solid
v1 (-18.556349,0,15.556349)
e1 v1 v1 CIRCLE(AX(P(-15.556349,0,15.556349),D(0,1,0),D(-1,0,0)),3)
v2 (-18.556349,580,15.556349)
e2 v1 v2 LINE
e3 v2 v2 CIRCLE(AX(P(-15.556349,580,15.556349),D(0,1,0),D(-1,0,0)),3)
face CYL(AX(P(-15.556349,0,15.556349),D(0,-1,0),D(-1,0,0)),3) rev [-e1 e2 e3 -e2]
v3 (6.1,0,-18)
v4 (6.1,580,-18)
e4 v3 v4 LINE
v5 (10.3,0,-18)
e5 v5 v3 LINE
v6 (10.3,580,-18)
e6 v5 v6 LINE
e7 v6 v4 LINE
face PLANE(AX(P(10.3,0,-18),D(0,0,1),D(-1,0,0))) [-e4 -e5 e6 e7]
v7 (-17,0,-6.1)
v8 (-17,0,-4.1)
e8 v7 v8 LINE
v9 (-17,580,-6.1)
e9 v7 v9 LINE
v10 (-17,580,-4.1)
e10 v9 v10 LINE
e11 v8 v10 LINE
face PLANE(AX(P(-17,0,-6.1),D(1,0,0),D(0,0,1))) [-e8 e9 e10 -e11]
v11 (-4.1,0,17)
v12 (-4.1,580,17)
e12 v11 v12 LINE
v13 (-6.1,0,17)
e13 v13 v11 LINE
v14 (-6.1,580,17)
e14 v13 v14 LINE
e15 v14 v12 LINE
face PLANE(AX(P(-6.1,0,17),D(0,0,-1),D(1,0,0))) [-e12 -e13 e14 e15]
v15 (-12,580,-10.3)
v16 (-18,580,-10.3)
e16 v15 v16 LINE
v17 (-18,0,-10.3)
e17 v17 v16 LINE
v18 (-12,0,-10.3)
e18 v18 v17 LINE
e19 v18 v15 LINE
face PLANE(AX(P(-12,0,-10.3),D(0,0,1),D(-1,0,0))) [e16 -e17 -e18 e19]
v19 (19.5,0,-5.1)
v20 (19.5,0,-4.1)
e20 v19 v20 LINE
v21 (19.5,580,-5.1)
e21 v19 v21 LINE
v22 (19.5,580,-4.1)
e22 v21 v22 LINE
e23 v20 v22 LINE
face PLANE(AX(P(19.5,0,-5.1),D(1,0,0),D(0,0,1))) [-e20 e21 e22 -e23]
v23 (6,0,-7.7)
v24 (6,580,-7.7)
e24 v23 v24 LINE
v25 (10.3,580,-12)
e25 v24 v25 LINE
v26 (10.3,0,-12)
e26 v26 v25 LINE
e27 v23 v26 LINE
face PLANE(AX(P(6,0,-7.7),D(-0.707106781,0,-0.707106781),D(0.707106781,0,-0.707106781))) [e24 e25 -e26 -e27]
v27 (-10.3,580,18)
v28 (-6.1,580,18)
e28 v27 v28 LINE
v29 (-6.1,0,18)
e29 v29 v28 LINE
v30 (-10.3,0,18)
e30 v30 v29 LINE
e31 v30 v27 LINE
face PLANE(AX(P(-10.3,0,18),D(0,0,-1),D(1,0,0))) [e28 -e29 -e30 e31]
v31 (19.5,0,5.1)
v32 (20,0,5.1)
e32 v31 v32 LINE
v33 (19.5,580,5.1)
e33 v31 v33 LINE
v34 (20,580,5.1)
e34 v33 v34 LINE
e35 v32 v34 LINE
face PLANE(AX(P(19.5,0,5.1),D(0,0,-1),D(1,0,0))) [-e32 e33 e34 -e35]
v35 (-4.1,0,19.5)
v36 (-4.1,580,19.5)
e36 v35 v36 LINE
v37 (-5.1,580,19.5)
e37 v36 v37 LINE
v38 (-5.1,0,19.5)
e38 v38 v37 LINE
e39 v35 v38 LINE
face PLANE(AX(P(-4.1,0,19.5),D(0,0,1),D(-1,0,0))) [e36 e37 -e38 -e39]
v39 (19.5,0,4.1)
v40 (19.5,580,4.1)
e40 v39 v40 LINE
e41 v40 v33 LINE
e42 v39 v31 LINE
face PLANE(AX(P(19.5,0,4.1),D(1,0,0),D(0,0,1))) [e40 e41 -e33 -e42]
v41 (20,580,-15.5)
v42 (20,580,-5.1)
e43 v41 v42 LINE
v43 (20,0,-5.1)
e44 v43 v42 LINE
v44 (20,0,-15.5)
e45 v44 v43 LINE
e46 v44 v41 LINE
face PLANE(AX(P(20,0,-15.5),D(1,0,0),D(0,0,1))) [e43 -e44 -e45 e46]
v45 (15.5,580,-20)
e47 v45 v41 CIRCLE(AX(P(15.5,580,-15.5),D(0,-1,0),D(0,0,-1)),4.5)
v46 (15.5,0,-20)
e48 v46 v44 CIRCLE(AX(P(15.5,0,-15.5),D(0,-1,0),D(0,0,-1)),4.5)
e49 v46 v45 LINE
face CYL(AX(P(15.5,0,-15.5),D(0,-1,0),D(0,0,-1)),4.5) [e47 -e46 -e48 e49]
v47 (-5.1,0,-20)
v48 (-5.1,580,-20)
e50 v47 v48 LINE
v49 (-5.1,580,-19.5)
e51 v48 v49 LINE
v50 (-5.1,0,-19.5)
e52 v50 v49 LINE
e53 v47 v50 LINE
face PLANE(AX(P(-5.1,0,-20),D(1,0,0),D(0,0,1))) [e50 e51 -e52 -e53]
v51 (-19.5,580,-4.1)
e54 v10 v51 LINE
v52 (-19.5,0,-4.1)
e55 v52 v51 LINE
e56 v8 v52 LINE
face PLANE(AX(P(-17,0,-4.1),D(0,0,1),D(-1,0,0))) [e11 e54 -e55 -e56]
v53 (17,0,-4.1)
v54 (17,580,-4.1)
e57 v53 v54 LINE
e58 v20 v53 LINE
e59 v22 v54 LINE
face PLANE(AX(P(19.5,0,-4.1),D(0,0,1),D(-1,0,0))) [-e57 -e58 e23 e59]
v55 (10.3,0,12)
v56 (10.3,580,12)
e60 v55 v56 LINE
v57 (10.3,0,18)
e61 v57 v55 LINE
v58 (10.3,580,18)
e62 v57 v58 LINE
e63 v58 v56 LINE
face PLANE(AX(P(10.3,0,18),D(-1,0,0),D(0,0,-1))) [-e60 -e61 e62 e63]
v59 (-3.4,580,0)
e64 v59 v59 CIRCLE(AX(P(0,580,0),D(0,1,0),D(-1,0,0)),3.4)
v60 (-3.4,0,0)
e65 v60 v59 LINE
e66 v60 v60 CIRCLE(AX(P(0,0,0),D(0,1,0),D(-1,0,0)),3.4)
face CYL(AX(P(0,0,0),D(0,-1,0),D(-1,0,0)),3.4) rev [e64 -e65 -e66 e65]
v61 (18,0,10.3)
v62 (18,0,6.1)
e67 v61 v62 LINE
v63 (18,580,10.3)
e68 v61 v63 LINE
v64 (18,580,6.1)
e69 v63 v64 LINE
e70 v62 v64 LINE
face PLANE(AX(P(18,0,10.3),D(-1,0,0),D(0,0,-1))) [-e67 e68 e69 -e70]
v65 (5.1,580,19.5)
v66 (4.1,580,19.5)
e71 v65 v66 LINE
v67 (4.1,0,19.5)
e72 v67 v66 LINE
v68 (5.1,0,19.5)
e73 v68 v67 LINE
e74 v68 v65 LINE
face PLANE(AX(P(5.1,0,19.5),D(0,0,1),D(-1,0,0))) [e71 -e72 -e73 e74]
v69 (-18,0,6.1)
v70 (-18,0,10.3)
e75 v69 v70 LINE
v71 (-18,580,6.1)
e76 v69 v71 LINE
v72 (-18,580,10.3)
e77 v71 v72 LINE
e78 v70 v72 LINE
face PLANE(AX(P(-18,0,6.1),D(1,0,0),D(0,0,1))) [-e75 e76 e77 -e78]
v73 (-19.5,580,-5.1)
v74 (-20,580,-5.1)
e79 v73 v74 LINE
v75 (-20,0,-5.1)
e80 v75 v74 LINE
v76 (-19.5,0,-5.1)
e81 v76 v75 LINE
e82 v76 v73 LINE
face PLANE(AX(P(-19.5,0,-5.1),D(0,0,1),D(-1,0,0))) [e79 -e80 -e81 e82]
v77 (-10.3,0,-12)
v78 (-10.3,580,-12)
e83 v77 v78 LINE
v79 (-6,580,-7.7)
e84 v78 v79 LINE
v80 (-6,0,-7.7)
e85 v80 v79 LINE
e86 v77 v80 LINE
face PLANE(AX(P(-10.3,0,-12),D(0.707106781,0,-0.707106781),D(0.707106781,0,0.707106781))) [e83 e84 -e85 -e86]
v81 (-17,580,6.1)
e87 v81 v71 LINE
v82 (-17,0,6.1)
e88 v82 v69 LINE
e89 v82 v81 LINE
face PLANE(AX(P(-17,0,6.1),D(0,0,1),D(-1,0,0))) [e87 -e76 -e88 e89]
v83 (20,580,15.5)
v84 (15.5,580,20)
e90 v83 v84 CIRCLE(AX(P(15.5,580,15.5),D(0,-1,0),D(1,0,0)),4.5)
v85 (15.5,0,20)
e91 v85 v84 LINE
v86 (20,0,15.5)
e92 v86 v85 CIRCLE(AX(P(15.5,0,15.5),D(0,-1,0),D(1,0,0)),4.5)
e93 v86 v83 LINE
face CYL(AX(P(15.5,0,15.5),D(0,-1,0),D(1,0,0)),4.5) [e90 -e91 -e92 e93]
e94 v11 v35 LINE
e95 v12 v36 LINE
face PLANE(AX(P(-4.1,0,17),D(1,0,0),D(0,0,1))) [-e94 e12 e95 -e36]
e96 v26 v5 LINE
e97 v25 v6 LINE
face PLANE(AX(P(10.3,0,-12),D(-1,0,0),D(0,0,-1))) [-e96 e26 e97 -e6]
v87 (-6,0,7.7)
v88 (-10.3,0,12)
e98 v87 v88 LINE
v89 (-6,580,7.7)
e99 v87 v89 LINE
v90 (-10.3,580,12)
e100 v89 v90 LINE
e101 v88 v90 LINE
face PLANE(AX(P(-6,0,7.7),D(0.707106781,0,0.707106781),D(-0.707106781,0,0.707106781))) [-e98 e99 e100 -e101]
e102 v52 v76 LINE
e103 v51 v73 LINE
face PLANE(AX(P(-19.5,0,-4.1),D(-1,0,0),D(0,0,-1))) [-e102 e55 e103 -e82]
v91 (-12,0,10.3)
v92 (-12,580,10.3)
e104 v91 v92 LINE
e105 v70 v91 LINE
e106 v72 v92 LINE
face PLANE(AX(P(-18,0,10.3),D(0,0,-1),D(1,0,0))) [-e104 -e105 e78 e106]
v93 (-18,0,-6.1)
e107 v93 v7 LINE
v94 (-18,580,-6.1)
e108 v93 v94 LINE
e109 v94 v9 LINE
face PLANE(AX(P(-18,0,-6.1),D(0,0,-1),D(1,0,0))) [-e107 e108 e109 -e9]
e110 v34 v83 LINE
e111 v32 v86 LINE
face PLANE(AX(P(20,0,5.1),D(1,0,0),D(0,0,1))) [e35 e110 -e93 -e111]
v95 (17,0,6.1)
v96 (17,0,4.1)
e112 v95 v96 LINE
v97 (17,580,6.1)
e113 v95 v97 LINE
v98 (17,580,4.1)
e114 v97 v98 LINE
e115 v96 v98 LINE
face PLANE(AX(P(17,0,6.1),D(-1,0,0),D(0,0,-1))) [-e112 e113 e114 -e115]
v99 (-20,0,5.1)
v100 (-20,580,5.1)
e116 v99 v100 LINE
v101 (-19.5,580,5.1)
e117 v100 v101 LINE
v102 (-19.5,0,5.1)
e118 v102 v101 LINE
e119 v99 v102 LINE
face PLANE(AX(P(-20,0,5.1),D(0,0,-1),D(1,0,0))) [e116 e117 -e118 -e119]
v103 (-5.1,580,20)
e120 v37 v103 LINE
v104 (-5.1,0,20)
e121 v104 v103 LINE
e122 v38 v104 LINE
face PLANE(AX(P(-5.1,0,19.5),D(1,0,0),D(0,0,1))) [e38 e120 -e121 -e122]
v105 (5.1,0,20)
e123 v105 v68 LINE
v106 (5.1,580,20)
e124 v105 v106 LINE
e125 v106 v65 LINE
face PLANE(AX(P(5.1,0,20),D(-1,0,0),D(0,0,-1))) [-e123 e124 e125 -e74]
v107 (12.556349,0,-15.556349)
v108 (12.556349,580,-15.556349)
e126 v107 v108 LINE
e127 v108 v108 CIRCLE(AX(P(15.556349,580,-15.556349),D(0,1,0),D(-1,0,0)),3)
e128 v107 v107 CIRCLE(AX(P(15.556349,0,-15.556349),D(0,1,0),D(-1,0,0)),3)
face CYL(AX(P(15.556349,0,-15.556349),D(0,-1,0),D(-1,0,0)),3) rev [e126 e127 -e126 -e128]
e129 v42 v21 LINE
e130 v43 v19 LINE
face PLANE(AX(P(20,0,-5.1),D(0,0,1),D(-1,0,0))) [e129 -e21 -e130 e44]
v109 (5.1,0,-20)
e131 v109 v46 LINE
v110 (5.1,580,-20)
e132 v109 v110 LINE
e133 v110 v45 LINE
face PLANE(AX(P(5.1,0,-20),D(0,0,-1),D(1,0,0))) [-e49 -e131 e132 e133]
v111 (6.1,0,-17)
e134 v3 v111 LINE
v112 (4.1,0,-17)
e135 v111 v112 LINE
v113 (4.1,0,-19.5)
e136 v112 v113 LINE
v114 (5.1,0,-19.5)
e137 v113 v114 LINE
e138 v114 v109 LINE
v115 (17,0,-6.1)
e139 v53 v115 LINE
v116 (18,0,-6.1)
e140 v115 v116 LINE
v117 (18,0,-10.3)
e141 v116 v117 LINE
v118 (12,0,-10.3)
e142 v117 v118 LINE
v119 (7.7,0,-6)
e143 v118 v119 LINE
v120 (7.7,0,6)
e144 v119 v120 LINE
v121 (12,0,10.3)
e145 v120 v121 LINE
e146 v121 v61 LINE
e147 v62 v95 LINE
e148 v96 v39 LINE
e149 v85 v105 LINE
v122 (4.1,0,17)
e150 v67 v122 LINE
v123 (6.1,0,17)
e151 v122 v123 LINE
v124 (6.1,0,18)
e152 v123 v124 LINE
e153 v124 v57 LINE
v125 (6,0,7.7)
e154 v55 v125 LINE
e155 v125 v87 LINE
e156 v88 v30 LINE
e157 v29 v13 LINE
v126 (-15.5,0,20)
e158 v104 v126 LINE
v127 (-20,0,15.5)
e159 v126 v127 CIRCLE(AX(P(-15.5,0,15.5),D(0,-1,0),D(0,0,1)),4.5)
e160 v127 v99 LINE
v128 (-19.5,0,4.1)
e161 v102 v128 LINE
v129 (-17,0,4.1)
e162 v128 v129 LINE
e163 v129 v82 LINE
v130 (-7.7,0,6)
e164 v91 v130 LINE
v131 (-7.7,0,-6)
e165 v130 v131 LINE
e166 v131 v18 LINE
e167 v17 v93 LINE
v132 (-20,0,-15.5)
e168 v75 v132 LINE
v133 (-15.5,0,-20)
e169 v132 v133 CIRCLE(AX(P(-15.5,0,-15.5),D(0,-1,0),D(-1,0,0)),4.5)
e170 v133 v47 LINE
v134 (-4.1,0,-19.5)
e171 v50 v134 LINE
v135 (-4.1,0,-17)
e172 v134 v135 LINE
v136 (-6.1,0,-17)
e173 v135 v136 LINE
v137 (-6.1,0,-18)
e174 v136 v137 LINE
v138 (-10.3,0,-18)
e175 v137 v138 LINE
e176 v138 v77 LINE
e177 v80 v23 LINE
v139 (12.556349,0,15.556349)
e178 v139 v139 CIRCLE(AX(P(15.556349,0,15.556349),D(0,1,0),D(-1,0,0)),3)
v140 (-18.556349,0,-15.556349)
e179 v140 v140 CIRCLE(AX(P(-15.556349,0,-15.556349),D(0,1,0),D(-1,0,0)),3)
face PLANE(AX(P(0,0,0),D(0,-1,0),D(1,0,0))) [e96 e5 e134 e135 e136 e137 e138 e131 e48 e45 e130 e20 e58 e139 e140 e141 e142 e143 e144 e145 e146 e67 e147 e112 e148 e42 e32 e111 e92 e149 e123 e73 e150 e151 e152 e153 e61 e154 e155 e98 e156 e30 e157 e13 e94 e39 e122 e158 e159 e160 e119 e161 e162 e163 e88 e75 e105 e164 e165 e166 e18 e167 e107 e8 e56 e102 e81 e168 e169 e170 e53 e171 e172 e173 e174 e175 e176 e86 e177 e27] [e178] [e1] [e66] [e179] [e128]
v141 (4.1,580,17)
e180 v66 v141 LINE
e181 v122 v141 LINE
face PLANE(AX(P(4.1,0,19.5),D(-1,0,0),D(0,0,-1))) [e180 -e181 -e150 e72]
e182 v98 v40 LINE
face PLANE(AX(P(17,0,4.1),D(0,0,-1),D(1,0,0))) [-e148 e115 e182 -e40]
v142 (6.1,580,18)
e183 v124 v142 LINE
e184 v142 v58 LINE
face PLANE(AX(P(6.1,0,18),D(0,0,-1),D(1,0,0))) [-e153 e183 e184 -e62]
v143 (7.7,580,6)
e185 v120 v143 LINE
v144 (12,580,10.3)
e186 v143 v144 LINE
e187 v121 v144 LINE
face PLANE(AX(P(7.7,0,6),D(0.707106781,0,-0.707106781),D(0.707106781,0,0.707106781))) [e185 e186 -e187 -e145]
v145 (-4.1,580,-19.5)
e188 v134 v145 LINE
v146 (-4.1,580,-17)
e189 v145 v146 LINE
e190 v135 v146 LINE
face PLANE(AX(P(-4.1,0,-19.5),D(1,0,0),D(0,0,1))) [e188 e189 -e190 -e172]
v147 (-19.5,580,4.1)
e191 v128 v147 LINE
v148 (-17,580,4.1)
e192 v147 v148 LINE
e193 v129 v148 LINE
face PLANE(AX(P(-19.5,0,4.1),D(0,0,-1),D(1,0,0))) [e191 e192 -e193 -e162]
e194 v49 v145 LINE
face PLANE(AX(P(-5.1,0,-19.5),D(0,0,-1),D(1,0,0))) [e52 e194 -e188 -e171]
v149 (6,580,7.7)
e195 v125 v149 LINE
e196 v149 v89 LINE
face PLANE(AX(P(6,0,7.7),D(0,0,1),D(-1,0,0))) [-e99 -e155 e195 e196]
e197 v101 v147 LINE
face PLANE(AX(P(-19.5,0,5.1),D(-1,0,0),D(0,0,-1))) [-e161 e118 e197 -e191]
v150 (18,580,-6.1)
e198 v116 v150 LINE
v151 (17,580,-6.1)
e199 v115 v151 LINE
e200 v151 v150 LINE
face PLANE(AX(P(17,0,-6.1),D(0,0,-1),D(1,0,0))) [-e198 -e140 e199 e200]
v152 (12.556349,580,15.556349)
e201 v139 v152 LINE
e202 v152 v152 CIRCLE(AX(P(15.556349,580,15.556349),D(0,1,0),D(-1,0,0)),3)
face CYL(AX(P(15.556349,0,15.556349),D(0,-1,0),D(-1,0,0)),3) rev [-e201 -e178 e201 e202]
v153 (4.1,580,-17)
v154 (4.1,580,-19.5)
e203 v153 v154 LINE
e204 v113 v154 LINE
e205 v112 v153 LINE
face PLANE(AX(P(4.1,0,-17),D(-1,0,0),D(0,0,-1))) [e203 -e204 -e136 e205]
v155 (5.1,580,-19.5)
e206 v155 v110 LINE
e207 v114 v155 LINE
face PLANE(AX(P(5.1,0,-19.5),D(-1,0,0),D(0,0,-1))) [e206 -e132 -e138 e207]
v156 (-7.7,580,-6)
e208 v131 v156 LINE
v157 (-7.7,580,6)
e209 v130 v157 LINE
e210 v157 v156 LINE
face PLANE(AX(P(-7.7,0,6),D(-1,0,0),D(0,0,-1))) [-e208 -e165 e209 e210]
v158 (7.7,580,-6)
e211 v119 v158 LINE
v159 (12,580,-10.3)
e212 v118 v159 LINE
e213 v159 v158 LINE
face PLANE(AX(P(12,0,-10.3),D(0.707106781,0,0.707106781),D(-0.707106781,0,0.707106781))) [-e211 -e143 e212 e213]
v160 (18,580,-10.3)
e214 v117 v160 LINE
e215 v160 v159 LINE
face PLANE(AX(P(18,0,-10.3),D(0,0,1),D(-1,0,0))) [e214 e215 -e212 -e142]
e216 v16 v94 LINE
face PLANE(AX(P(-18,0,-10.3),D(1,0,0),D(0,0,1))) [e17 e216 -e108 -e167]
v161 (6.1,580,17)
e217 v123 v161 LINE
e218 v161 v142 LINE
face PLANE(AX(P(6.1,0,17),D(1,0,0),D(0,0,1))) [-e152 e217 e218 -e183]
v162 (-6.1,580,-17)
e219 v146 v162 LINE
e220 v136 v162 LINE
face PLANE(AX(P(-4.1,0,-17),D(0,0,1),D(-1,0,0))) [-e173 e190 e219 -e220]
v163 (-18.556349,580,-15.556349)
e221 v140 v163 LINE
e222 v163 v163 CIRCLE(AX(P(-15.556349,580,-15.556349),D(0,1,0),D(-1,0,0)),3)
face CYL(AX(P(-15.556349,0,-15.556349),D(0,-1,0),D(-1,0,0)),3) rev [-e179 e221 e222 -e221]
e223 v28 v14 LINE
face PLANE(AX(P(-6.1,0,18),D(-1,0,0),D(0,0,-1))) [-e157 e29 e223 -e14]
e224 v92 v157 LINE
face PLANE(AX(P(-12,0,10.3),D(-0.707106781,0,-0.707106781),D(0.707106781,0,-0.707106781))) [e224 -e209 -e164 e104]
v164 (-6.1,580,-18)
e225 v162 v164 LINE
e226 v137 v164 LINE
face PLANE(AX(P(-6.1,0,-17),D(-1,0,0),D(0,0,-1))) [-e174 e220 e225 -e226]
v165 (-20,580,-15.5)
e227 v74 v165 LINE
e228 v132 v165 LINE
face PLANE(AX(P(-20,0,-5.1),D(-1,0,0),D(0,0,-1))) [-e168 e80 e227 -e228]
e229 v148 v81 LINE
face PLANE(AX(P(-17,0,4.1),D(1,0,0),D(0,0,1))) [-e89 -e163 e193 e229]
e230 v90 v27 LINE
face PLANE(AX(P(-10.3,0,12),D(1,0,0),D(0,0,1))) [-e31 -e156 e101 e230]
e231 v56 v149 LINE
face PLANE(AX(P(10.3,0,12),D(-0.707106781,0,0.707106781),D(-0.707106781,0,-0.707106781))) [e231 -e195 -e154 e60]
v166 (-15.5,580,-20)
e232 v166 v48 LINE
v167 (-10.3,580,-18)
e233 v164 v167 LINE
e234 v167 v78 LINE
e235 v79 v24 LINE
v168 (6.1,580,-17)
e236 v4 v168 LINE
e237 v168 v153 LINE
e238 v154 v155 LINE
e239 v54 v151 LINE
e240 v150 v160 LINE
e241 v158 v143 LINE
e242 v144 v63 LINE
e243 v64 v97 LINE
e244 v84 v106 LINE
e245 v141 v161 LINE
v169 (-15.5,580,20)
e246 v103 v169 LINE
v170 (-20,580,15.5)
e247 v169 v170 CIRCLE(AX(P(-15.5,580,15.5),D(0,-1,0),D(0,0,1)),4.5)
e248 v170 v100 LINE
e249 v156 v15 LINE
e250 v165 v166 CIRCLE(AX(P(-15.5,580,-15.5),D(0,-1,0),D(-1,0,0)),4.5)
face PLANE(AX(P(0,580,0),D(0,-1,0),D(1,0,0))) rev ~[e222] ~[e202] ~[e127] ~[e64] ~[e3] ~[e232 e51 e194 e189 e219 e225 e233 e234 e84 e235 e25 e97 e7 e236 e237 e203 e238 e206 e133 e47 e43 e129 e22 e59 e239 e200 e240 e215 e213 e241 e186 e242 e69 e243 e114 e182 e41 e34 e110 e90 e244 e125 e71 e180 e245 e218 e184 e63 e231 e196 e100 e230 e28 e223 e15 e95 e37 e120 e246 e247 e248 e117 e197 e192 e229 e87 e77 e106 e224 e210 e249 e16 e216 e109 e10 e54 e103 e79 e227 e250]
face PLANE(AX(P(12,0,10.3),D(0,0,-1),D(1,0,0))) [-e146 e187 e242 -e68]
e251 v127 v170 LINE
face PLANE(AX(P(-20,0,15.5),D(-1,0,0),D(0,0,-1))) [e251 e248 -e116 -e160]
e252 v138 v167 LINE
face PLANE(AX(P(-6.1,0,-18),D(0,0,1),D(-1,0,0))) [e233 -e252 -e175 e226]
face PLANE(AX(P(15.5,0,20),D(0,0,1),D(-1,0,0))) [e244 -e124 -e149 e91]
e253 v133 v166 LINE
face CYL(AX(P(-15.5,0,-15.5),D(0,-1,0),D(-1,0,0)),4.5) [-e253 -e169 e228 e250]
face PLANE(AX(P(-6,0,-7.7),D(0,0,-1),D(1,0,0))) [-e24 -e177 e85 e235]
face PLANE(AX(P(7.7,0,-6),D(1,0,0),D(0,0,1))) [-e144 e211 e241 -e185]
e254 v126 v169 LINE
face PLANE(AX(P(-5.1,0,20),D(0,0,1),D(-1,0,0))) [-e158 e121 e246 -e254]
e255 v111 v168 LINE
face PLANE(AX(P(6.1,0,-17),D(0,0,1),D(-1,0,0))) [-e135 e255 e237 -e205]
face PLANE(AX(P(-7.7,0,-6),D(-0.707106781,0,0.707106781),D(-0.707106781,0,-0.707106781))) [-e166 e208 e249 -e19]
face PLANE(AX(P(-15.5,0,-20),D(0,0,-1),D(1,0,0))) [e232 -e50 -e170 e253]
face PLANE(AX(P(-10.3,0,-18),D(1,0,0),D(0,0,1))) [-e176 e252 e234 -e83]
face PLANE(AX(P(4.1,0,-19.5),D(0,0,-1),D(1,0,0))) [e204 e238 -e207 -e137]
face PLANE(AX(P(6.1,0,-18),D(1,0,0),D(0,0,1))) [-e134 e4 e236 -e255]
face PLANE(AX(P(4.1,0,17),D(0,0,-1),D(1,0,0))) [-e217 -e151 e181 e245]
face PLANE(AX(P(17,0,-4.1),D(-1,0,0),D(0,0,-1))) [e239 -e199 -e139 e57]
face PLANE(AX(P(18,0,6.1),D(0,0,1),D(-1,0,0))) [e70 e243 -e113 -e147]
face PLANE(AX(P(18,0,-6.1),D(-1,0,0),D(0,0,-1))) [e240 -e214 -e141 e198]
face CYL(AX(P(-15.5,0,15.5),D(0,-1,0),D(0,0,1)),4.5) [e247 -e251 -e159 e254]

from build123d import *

# Parameters (mm, degrees)
SKETCH16_R     = 3.4
SKETCH16_R_2   = 3
MEMBER_1_DEPTH = 580


with BuildPart() as part:
    # Sketch16 → Member 1 (new body)
    with BuildSketch(Plane(origin=(0, 0, 0), x_dir=(-1, 0, 0), z_dir=(0, 1, 0))):
        with BuildLine():
            Line((-5.1, 20), (-5.1, 19.5))
            Line((-5.1, 19.5), (-4.1, 19.5))
            Line((-4.1, 19.5), (-4.1, 17))
            Line((-4.1, 17), (-6.1, 17))
            Line((-6.1, 17), (-6.1, 18))
            Line((-6.1, 18), (-10.3, 18))
            Line((-10.3, 18), (-10.3, 12))
            Line((-10.3, 12), (-6, 7.7))
            Line((-6, 7.7), (6, 7.7))
            Line((6, 7.7), (10.3, 12))
            Line((10.3, 12), (10.3, 18))
            Line((10.3, 18), (6.1, 18))
            Line((6.1, 18), (6.1, 17))
            Line((6.1, 17), (4.1, 17))
            Line((4.1, 17), (4.1, 19.5))
            Line((4.1, 19.5), (5.1, 19.5))
            Line((5.1, 19.5), (5.1, 20))
            Line((5.1, 20), (15.5, 20))
            ThreePointArc((15.5, 20), (18.681980515, 18.681980515), (20, 15.5))
            Line((20, 15.5), (20, 5.1))
            Line((20, 5.1), (19.5, 5.1))
            Line((19.5, 5.1), (19.5, 4.1))
            Line((19.5, 4.1), (17, 4.1))
            Line((17, 4.1), (17, 6.1))
            Line((17, 6.1), (18, 6.1))
            Line((18, 6.1), (18, 10.3))
            Line((18, 10.3), (12, 10.3))
            Line((12, 10.3), (7.7, 6))
            Line((7.7, 6), (7.7, -6))
            Line((7.7, -6), (12, -10.3))
            Line((12, -10.3), (18, -10.3))
            Line((18, -10.3), (18, -6.1))
            Line((18, -6.1), (17, -6.1))
            Line((17, -6.1), (17, -4.1))
            Line((17, -4.1), (19.5, -4.1))
            Line((19.5, -4.1), (19.5, -5.1))
            Line((19.5, -5.1), (20, -5.1))
            Line((20, -5.1), (20, -15.5))
            ThreePointArc((20, -15.5), (18.681980515, -18.681980515), (15.5, -20))
            Line((15.5, -20), (5.1, -20))
            Line((5.1, -20), (5.1, -19.5))
            Line((5.1, -19.5), (4.1, -19.5))
            Line((4.1, -19.5), (4.1, -17))
            Line((4.1, -17), (6.1, -17))
            Line((6.1, -17), (6.1, -18))
            Line((6.1, -18), (10.3, -18))
            Line((10.3, -18), (10.3, -12))
            Line((10.3, -12), (6, -7.7))
            Line((6, -7.7), (-6, -7.7))
            Line((-6, -7.7), (-10.3, -12))
            Line((-10.3, -12), (-10.3, -18))
            Line((-10.3, -18), (-6.1, -18))
            Line((-6.1, -18), (-6.1, -17))
            Line((-6.1, -17), (-4.1, -17))
            Line((-4.1, -17), (-4.1, -19.5))
            Line((-4.1, -19.5), (-5.1, -19.5))
            Line((-5.1, -19.5), (-5.1, -20))
            Line((-5.1, -20), (-15.5, -20))
            ThreePointArc((-15.5, -20), (-18.681980515, -18.681980515), (-20, -15.5))
            Line((-20, -15.5), (-20, -5.1))
            Line((-20, -5.1), (-19.5, -5.1))
            Line((-19.5, -5.1), (-19.5, -4.1))
            Line((-19.5, -4.1), (-17, -4.1))
            Line((-17, -4.1), (-17, -6.1))
            Line((-17, -6.1), (-18, -6.1))
            Line((-18, -6.1), (-18, -10.3))
            Line((-18, -10.3), (-12, -10.3))
            Line((-12, -10.3), (-7.7, -6))
            Line((-7.7, -6), (-7.7, 6))
            Line((-7.7, 6), (-12, 10.3))
            Line((-12, 10.3), (-18, 10.3))
            Line((-18, 10.3), (-18, 6.1))
            Line((-18, 6.1), (-17, 6.1))
            Line((-17, 6.1), (-17, 4.1))
            Line((-17, 4.1), (-19.5, 4.1))
            Line((-19.5, 4.1), (-19.5, 5.1))
            Line((-19.5, 5.1), (-20, 5.1))
            Line((-20, 5.1), (-20, 15.5))
            ThreePointArc((-20, 15.5), (-18.681980515, 18.681980515), (-15.5, 20))
            Line((-15.5, 20), (-5.1, 20))
        make_face()
        Circle(SKETCH16_R, mode=Mode.SUBTRACT)
        with Locations((-15.556349186, 15.556349186)):
            Circle(SKETCH16_R_2, mode=Mode.SUBTRACT)
        with Locations((15.556349186, 15.556349186)):
            Circle(SKETCH16_R_2, mode=Mode.SUBTRACT)
        with Locations((15.556349186, -15.556349186)):
            Circle(SKETCH16_R_2, mode=Mode.SUBTRACT)
        with Locations((-15.556349186, -15.556349186)):
            Circle(SKETCH16_R_2, mode=Mode.SUBTRACT)
    extrude(amount=MEMBER_1_DEPTH)


solid = part.part
